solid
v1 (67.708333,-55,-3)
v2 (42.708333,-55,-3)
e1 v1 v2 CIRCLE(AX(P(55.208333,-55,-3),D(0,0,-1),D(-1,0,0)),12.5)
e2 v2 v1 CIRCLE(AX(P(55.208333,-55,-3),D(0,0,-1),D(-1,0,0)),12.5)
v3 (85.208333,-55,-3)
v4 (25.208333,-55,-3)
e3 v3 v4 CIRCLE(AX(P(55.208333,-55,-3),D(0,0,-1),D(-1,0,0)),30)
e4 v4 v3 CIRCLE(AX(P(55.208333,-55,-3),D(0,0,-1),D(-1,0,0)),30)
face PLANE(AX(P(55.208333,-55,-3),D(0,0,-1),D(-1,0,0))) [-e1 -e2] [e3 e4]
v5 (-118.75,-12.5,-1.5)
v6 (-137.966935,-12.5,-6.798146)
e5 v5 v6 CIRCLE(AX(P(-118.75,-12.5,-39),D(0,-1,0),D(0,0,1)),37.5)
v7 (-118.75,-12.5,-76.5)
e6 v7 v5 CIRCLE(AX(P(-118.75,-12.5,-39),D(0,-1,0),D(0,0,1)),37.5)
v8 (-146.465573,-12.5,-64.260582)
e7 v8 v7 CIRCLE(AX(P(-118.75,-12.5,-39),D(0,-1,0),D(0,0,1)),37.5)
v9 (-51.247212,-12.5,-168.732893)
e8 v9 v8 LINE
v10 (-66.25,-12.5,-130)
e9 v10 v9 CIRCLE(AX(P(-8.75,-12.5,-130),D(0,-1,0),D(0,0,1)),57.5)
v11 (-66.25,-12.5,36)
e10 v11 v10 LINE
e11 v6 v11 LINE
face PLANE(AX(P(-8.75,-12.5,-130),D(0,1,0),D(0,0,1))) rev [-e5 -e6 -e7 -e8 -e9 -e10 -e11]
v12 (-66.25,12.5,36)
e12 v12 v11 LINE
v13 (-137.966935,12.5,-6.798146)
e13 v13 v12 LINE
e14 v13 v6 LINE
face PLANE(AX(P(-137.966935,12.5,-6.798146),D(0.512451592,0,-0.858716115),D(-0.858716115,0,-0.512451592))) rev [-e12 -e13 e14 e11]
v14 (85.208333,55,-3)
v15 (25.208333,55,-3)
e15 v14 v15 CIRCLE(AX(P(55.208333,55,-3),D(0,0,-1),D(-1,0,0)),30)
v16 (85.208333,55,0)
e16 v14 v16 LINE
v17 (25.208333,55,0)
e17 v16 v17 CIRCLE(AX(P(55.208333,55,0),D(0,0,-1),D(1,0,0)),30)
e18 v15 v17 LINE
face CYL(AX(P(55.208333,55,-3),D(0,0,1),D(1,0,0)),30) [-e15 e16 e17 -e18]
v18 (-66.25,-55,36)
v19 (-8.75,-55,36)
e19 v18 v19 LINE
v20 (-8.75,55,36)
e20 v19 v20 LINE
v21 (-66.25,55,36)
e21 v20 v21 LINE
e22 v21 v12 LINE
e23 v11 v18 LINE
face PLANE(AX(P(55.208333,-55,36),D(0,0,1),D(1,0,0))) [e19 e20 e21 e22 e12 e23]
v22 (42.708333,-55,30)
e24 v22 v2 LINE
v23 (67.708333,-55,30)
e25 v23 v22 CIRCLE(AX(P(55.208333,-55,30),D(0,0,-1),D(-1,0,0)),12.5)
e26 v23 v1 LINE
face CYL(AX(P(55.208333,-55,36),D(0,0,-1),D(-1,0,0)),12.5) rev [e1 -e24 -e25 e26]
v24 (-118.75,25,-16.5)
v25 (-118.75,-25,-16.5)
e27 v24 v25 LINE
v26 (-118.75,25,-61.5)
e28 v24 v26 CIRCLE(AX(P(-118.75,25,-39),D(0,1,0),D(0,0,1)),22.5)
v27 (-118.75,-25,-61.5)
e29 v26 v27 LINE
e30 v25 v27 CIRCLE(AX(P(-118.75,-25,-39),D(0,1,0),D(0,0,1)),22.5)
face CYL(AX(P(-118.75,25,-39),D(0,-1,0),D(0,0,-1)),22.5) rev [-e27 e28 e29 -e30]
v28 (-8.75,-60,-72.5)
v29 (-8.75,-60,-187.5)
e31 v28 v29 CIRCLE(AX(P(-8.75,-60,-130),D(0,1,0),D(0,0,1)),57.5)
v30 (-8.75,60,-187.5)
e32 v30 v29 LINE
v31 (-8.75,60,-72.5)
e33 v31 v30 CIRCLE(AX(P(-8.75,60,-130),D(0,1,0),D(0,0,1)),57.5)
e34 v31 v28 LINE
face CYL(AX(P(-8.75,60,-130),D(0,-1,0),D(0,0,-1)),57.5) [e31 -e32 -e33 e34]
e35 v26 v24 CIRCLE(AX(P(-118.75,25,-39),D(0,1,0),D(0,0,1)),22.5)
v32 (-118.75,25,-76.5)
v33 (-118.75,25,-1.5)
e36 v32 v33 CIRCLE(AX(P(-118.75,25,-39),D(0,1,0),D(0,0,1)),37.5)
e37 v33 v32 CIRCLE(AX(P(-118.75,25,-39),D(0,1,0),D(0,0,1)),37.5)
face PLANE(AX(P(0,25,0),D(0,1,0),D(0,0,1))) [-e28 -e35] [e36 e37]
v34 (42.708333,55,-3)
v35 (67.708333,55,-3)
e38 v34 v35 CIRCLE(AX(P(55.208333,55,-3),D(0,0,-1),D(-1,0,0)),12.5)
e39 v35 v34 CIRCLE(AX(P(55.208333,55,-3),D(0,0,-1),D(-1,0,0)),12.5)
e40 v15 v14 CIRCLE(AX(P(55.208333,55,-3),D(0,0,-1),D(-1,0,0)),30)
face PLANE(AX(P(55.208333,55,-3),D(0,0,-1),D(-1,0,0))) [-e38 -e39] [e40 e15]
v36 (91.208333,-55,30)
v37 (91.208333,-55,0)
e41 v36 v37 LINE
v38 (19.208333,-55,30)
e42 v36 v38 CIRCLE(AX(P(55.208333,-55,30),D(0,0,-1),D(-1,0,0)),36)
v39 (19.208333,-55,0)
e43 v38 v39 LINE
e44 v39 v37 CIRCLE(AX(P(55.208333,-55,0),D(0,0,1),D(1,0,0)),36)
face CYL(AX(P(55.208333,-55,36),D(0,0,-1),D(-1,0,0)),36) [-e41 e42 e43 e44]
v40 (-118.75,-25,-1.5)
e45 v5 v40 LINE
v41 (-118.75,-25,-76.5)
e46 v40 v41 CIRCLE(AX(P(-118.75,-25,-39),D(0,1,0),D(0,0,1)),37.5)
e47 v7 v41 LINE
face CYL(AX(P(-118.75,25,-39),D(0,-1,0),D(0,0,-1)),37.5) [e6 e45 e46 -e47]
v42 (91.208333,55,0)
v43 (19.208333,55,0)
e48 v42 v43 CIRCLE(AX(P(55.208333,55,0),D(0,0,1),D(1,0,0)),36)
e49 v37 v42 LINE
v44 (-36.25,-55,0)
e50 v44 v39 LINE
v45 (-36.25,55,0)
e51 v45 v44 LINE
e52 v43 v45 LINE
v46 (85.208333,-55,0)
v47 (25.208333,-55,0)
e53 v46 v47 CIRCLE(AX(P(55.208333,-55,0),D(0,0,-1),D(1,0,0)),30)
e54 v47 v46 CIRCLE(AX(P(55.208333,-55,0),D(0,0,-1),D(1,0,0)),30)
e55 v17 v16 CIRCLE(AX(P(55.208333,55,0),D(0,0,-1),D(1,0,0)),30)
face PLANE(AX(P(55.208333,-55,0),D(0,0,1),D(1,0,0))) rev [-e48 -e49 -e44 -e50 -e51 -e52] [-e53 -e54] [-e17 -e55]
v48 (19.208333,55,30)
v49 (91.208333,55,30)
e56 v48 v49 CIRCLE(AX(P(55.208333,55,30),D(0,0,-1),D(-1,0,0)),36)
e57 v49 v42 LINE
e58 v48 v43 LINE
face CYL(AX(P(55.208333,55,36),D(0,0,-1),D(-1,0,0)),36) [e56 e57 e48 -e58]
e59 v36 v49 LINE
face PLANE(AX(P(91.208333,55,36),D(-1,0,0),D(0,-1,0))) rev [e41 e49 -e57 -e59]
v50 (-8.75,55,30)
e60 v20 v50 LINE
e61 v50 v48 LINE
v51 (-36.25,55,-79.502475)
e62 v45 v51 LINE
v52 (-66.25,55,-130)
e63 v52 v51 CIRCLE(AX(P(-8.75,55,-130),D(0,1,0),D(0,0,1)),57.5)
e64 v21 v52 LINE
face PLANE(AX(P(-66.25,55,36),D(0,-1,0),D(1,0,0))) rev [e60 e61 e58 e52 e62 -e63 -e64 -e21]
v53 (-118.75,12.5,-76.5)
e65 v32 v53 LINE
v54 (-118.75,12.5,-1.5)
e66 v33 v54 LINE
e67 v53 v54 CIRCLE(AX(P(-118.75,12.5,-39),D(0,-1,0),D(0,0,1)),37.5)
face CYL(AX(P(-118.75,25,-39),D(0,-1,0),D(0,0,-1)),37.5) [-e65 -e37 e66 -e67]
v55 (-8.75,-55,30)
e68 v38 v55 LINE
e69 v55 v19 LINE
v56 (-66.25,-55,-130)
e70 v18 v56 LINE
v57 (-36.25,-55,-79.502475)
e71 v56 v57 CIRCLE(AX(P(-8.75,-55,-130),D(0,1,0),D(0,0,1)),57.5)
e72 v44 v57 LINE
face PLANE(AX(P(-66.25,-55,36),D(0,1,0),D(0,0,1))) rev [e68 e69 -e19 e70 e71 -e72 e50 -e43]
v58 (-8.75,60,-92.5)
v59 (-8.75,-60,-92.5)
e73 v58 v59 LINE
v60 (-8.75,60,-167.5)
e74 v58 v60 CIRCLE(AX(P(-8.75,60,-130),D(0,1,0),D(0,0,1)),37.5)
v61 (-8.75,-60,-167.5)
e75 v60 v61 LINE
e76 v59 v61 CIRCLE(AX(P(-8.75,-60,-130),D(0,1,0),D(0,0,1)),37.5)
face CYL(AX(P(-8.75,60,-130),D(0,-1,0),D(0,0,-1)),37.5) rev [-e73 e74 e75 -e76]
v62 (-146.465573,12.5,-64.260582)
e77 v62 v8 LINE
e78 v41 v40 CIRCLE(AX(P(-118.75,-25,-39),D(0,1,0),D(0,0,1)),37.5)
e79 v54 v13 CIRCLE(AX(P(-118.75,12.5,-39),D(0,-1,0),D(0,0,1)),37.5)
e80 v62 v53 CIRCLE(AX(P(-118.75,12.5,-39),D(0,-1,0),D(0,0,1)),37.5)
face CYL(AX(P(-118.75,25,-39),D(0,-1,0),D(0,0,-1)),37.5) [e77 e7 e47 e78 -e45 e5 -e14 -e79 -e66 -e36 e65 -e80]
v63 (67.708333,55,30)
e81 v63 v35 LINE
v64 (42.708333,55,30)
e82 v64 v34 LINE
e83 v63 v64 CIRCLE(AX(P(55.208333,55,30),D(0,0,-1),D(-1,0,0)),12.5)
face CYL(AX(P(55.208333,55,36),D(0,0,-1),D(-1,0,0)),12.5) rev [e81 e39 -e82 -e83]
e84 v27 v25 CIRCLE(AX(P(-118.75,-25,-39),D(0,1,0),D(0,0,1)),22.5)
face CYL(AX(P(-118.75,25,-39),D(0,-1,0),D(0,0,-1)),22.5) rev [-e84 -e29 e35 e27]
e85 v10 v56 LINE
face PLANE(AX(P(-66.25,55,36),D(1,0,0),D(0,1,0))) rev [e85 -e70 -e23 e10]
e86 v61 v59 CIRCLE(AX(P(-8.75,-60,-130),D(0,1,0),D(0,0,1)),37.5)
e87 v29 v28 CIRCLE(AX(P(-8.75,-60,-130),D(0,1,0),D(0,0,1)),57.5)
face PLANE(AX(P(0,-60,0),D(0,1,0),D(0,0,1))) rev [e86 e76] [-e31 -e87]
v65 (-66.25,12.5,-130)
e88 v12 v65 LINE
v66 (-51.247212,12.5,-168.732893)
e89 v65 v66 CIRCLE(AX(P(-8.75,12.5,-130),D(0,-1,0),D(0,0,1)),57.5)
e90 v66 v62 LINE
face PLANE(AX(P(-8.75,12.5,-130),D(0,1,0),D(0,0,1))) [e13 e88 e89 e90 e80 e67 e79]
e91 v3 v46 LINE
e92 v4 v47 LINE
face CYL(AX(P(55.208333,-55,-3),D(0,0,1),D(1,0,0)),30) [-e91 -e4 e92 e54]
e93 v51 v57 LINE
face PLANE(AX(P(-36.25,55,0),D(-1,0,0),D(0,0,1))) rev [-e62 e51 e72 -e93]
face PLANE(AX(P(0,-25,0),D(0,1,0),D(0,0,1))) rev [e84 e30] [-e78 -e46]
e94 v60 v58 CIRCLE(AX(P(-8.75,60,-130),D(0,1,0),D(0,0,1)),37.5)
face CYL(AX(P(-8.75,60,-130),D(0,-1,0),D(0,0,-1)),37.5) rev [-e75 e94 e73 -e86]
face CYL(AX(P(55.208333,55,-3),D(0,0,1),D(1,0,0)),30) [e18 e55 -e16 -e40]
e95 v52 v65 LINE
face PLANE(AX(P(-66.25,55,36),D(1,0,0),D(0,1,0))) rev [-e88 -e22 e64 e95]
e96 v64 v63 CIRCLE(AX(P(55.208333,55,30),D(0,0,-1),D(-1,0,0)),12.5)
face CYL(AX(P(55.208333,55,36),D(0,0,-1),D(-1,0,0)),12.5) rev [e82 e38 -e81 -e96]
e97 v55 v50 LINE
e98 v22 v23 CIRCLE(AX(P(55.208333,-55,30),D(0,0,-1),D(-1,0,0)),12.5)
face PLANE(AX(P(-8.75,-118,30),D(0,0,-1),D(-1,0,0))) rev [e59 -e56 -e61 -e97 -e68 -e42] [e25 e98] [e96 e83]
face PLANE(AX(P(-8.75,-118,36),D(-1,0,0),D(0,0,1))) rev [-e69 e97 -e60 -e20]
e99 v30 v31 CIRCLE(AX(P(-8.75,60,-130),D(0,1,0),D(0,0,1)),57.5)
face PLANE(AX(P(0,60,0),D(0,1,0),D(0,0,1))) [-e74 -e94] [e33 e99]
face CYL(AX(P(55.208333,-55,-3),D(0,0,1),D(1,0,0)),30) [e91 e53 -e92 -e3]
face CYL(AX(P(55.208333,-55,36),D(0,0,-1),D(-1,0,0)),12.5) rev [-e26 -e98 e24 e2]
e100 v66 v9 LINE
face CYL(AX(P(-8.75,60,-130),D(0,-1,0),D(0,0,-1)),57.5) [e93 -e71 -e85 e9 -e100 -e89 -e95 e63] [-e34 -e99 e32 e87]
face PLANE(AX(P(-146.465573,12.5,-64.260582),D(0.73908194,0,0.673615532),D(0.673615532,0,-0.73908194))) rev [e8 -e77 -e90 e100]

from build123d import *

# Parameters (mm, degrees)
BASE_PROFILE_SKETCH_R    = 12.5
BASE_BODY_DEPTH          = 36
SLOT_CUT_DEPTH           = 118
ARM_PROFILE_SKETCH_R     = 57.5
ARM_PROFILE_SKETCH_R_2   = 37.5
ARM_BOSS_DEPTH           = 60
ARM_BOSS_REGION_2_DEPTH  = 55
HUB_SKETCH_R             = 37.5
HUB_SKETCH_R_2           = 22.5
HUB_BOSS_DEPTH           = 25
SUPPORT_WEB_DEPTH        = 12.5
PAD_SKETCH_60X60_R       = 30
PAD_SKETCH_60X60_R_2     = 12.5
MOUNTING_PAD_60X60_DEPTH = 3


with BuildPart() as part:
    # Base Profile Sketch → Base Body (new body)
    with BuildSketch(Plane.XY):
        with BuildLine():
            Line((-66.25, 55), (19.208333333, 55))
            ThreePointArc((19.208333333, 55), (55.208333333, 91), (91.208333333, 55))
            Line((91.208333333, 55), (91.208333333, -55))
            ThreePointArc((91.208333333, -55), (55.208333333, -91), (19.208333333, -55))
            Line((19.208333333, -55), (-66.25, -55))
            Line((-66.25, -55), (-66.25, 55))
        make_face()
        with Locations((55.208333333, 55)):
            Circle(BASE_PROFILE_SKETCH_R, mode=Mode.SUBTRACT)
        with Locations((55.208333333, -55)):
            Circle(BASE_PROFILE_SKETCH_R, mode=Mode.SUBTRACT)
    extrude(amount=BASE_BODY_DEPTH)

    # Slot Sketch → Slot Cut (cut, symmetric)
    with BuildSketch(Plane(origin=(0, 0, 0), x_dir=(1, 0, 0), z_dir=(0, 1, 0))):
        Polygon((-8.75, -36), (-8.75, -30), (91.208333333, -30), (91.208333333, -36), (19.208333333, -36), align=None)
    extrude(amount=SLOT_CUT_DEPTH, both=True, mode=Mode.SUBTRACT)



with BuildPart() as body_2:
    # Arm Profile Sketch → Arm Boss (new, symmetric)
    with BuildSketch(Plane(origin=(0, 0, 0), x_dir=(1, 0, 0), z_dir=(0, 1, 0))):
        with Locations(Location((-8.75, 130, 0), (0, 0, 270))):
            Circle(ARM_PROFILE_SKETCH_R)
        with Locations(Location((-8.75, 130, 0), (0, 0, 270))):
            Circle(ARM_PROFILE_SKETCH_R_2, mode=Mode.SUBTRACT)
    extrude(amount=ARM_BOSS_DEPTH, both=True)


with BuildPart() as part_1:
    add(part.part)

    add(body_2.part)  # Arm Boss Region 2 merges body 2
    # Sketch4_3 → Arm Boss Region 2 (add, symmetric)
    with BuildSketch(Plane(origin=(0, 0, 0), x_dir=(1, 0, 0), z_dir=(0, 1, 0))):
        with BuildLine():
            Line((-66.25, 130), (-66.25, 0))
            Line((-66.25, 0), (-36.25, 0))
            Line((-36.25, 0), (-36.25, 79.502475308))
            ThreePointArc((-36.25, 79.502475308), (-58.184299833, 100.631649689), (-66.25, 130))
        make_face()
    extrude(amount=ARM_BOSS_REGION_2_DEPTH, both=True)



with BuildPart() as body_2_2:
    # Hub Sketch → Hub Boss (new, symmetric)
    with BuildSketch(Plane(origin=(0, 0, 0), x_dir=(1, 0, 0), z_dir=(0, 1, 0))):
        with Locations(Location((-118.75, 39, 0), (0, 0, 270))):
            Circle(HUB_SKETCH_R)
        with Locations(Location((-118.75, 39, 0), (0, 0, 270))):
            Circle(HUB_SKETCH_R_2, mode=Mode.SUBTRACT)
    extrude(amount=HUB_BOSS_DEPTH, both=True)


with BuildPart() as part_2:
    add(part_1.part)

    add(body_2_2.part)  # Support Web merges body 2 2
    # Web Sketch → Support Web (add, symmetric)
    with BuildSketch(Plane(origin=(0, 0, 0), x_dir=(1, 0, 0), z_dir=(0, 1, 0))):
        with BuildLine():
            Line((-146.465572764, 64.260582462), (-51.247211572, 168.732893109))
            ThreePointArc((-51.247211572, 168.732893109), (-62.368278905, 150.768489769), (-66.25, 130))
            Line((-66.25, 130), (-66.25, -36))
            Line((-66.25, -36), (-137.966934712, 6.798145701))
            ThreePointArc((-137.966934712, 6.798145701), (-81.653531514, 44.486531314), (-146.465572764, 64.260582462))
        make_face()
    extrude(amount=SUPPORT_WEB_DEPTH, both=True)

    # Pad Sketch 60x60 → Mounting Pad 60x60 (add, symmetric)
    # profile 1 of 2: a face of its own
    with BuildSketch(Plane(origin=(0, 0, 0), x_dir=(-1, 0, 0), z_dir=(0, 0, -1))):
        with Locations(Location((-55.208333333, 55, 0), (0, 0, 180))):
            Circle(PAD_SKETCH_60X60_R)
        with Locations((-55.208333333, 55)):
            Circle(PAD_SKETCH_60X60_R_2, mode=Mode.SUBTRACT)
    # profile 2 of 2: a face of its own
    with BuildSketch(Plane(origin=(0, 0, 0), x_dir=(-1, 0, 0), z_dir=(0, 0, -1))):
        with Locations(Location((-55.208333333, -55, 0), (0, 0, 180))):
            Circle(PAD_SKETCH_60X60_R)
        with Locations((-55.208333333, -55)):
            Circle(PAD_SKETCH_60X60_R_2, mode=Mode.SUBTRACT)
    extrude(amount=MOUNTING_PAD_60X60_DEPTH, both=True)


solid = part_2.part
